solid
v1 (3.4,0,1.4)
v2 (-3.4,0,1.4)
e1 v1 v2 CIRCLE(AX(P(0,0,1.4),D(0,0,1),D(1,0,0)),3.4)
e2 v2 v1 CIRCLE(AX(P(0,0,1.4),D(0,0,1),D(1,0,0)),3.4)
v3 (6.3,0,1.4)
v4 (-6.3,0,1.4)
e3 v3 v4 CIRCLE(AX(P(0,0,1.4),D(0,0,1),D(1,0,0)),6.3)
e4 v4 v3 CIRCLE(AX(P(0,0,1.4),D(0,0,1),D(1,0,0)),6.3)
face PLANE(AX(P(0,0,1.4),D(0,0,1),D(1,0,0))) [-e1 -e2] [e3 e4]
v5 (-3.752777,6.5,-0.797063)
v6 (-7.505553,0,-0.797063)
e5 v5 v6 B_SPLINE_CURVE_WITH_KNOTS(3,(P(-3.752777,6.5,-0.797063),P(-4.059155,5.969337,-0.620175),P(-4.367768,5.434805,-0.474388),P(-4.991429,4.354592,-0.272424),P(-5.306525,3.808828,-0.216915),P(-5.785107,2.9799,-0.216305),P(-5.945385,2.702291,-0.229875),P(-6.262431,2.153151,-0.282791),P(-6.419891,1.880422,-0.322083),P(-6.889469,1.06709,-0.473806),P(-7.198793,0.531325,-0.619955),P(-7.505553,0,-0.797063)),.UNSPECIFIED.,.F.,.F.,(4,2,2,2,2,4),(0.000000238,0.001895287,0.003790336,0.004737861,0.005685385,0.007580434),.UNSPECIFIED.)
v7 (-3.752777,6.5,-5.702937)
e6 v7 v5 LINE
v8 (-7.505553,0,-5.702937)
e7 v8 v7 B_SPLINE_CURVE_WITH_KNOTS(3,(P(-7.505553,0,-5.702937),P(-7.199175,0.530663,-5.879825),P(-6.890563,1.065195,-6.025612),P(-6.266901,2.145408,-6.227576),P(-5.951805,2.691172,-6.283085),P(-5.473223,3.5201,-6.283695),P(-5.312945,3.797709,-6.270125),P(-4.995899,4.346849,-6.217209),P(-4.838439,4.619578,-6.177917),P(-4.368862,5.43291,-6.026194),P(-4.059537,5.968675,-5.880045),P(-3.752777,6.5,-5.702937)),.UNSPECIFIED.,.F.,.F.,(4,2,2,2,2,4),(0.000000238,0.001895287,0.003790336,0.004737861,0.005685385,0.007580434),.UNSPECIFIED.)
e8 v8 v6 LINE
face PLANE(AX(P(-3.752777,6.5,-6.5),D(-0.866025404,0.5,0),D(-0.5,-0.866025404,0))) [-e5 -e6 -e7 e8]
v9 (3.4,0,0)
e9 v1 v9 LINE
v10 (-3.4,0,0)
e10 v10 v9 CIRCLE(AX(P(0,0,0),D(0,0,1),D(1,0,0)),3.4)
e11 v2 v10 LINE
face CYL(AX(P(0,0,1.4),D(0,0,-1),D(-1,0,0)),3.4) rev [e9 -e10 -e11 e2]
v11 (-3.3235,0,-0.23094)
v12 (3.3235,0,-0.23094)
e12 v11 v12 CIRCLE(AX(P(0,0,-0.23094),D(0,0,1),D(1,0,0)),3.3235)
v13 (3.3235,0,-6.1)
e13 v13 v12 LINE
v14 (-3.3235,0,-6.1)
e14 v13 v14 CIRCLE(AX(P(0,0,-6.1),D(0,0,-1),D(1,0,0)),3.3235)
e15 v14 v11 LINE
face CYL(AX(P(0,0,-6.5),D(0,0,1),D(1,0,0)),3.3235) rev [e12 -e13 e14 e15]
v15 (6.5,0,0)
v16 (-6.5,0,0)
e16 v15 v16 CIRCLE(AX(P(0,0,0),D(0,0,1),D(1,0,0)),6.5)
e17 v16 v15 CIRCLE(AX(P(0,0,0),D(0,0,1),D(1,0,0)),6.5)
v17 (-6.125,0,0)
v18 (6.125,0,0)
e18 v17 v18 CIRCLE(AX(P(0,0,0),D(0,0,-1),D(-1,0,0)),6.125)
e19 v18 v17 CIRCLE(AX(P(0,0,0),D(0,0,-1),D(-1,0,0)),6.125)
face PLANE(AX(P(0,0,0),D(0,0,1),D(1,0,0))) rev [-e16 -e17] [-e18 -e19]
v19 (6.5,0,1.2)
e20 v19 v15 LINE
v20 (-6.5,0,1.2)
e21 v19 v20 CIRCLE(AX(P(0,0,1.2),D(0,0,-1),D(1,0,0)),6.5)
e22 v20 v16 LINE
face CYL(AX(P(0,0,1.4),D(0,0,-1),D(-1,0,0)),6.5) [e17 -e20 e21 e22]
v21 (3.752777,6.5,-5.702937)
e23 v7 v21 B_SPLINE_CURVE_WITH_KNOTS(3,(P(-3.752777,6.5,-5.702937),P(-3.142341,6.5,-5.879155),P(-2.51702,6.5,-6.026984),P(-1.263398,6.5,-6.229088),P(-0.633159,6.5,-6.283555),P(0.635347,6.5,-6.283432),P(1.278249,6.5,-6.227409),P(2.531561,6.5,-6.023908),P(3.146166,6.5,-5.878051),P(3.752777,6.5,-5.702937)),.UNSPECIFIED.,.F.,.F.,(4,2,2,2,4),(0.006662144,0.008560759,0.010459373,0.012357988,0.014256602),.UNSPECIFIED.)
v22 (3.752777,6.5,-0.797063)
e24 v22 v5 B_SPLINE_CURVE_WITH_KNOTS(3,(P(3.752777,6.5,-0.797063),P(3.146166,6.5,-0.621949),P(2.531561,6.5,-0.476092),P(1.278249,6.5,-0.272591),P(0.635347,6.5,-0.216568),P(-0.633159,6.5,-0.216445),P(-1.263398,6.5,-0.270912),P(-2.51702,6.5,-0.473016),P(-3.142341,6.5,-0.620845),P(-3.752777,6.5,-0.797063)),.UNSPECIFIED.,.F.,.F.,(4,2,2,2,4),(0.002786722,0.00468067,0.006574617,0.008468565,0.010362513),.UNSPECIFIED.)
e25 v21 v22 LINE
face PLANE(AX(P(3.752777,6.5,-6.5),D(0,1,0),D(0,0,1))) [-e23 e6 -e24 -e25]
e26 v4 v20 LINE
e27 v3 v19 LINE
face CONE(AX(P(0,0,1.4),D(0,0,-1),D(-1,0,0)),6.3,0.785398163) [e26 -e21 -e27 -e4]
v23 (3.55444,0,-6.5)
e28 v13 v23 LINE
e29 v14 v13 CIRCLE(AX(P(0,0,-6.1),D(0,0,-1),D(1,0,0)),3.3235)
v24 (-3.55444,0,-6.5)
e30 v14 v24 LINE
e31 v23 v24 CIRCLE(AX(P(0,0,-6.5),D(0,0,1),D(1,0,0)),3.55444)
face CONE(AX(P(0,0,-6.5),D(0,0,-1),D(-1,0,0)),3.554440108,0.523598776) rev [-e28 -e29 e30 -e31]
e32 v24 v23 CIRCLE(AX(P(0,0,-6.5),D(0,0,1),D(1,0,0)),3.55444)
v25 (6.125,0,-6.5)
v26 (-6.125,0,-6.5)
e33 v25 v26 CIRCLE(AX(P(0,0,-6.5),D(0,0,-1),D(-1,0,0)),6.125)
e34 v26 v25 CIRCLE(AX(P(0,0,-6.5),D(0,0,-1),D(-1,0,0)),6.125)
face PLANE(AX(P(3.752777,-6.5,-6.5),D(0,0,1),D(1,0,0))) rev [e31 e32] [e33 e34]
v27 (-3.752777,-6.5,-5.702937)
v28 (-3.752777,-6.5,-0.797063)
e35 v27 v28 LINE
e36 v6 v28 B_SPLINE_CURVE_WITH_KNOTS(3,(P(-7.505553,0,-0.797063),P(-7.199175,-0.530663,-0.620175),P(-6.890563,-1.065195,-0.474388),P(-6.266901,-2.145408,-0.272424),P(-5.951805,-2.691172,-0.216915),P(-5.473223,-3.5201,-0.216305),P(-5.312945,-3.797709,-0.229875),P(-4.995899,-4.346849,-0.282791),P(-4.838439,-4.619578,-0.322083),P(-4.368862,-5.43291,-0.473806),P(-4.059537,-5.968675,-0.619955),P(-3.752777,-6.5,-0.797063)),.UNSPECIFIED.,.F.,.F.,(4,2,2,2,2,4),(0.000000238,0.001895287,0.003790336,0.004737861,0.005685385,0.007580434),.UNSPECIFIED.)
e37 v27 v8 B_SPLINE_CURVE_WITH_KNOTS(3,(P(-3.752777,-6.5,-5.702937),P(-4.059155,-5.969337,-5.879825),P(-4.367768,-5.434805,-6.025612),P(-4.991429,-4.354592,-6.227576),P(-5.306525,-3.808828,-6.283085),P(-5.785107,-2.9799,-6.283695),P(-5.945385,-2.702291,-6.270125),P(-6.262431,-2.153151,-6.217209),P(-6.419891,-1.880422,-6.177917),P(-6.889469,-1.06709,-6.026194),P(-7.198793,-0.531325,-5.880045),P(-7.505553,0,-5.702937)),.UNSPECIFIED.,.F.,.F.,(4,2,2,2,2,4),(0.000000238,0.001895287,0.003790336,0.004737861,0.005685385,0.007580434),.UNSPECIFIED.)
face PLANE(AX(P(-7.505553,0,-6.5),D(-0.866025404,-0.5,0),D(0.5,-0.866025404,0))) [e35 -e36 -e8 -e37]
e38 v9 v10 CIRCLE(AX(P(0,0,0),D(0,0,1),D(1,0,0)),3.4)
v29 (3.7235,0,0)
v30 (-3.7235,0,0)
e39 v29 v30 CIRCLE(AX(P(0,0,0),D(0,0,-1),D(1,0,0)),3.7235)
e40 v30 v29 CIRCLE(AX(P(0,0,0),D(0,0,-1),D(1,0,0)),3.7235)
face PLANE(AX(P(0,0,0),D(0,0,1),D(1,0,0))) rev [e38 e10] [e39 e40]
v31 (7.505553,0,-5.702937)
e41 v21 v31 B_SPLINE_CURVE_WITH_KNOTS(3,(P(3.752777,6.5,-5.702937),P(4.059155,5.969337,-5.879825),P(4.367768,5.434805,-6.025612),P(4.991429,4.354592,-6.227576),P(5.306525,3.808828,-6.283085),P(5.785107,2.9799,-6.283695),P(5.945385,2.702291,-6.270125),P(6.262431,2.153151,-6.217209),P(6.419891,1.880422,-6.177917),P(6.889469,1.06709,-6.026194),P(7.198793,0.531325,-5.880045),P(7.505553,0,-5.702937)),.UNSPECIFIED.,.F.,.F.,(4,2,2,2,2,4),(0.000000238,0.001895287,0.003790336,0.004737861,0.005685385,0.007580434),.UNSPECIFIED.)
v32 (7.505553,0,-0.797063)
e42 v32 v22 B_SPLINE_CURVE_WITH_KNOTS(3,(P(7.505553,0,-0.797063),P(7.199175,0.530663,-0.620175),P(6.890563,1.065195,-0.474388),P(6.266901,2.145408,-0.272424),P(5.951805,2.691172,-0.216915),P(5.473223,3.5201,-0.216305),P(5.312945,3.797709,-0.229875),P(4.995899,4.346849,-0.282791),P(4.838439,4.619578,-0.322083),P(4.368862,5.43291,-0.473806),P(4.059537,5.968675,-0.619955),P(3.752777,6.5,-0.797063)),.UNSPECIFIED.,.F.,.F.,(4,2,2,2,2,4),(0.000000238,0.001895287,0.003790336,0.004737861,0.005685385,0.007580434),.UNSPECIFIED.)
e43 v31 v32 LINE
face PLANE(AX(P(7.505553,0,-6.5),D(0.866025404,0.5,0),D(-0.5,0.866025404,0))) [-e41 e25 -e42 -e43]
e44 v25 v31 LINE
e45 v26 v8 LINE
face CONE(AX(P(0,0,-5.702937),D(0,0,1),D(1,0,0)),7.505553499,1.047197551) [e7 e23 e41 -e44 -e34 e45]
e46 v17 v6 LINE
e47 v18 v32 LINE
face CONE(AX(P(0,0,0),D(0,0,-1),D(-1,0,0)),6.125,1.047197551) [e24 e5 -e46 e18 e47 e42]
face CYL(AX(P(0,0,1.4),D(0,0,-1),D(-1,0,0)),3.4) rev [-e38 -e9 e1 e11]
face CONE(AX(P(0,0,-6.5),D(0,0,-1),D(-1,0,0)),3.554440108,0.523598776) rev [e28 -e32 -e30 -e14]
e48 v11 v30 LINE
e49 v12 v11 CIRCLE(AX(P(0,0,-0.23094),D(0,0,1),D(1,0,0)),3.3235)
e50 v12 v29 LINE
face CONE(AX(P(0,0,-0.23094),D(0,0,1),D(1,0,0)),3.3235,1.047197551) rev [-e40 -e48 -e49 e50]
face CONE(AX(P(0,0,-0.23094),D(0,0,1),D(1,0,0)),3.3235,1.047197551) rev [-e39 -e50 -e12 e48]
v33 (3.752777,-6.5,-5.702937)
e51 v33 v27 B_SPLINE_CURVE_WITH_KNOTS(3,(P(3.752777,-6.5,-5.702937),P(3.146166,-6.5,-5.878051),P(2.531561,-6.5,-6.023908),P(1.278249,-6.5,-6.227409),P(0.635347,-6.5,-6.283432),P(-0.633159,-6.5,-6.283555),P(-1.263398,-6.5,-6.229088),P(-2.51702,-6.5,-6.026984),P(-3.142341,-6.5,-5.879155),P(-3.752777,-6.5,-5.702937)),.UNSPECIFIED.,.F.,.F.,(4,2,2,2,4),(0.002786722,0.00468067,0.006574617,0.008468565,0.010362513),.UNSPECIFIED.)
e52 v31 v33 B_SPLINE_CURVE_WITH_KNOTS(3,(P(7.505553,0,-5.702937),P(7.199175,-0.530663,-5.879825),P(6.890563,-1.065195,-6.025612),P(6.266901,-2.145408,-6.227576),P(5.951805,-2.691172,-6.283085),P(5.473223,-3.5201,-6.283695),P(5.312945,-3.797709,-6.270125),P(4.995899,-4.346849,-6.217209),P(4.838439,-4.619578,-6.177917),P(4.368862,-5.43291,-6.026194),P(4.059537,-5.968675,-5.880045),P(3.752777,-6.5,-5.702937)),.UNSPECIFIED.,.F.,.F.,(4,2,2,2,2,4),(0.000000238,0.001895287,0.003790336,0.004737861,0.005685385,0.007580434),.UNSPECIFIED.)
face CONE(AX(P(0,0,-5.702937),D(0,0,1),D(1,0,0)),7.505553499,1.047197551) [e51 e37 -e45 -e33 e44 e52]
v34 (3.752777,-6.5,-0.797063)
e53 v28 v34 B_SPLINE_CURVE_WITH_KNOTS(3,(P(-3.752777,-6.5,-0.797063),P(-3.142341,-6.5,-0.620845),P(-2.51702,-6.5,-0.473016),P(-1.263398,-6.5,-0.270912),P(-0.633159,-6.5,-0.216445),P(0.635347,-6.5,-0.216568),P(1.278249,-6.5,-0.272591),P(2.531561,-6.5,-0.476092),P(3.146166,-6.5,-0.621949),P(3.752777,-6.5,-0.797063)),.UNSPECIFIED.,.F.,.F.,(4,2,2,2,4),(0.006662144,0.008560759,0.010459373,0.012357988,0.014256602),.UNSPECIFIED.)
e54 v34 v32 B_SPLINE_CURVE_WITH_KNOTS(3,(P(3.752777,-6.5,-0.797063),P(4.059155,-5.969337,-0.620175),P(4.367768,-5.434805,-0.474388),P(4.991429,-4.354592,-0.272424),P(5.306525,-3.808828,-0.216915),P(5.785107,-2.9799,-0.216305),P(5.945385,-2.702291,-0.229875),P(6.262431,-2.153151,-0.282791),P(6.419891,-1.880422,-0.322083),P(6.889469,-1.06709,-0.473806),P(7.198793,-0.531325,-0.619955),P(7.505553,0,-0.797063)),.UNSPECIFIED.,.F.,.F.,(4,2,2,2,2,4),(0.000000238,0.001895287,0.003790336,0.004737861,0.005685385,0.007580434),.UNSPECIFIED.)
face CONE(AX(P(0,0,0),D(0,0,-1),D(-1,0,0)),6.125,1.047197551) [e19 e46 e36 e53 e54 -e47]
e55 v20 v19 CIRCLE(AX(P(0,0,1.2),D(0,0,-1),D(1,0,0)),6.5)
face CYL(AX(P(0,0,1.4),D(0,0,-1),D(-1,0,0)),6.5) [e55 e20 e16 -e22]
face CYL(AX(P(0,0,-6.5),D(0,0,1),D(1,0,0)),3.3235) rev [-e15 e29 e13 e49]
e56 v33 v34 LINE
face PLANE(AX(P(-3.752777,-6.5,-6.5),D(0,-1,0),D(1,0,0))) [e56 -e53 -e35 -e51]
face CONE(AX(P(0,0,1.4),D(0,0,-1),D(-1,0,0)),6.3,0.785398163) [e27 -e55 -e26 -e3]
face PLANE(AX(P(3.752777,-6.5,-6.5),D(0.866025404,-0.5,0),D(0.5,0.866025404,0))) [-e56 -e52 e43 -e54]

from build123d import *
from OCP.BRepFilletAPI import BRepFilletAPI_MakeChamfer

# Parameters (mm, degrees)
SKETCH1_R        = 3.3235
BASENUT_DEPTH    = 6.5
ENDCHAMFER_SIZE  = 0.4
ENDCHAMFER_SIZE2 = 0.230940108
SKETCH_1_R       = 6.5
SKETCH_1_R_2     = 3.4
EXTRUDE_1_DEPTH  = 1.4
CHAMFER_1_SIZE   = 0.2


with BuildPart() as part:
    # Sketch1 → BaseNut (new body)
    with BuildSketch(Plane.XY):
        Polygon((3.75277675, -6.5), (7.505553499, 0), (3.75277675, 6.5), (-3.75277675, 6.5), (-7.505553499, 0), (-3.75277675, -6.5), align=None)
        Circle(SKETCH1_R, mode=Mode.SUBTRACT)
    extrude(amount=-BASENUT_DEPTH)

    # Sketch2 → Double-Chamfer (revolve, cut)
    with BuildSketch(Plane(origin=(0, 0, 0), x_dir=(1, 0, 0), z_dir=(0, 1, 0))):
        Polygon((-7.505553499, 6.5), (-6.125, 6.5), (-7.505553499, 5.702937065), align=None)
        Polygon((-7.505553499, 0.797062935), (-7.505553499, 0), (-6.125, 0), align=None)
    revolve(axis=Axis((0, 0, -3.375940562), (0, 0, 1)), mode=Mode.SUBTRACT)

    # EndChamfer: one chamfer whose edges measure the first distance from different faces: ONE call of the kernel's chamfer builder (chamfer() names one face for all edges)
    endchamfer_edges_1 = [part.edges().sort_by_distance(p)[0] for p in [
        (-3.3235, 0, -6.5),
    ]]
    endchamfer_side_1 = [part.faces().sort_by_distance(p)[0] for p in [
        (-3.3235, 0, -3.25),
    ]]
    endchamfer_edges_2 = [part.edges().sort_by_distance(p)[0] for p in [
        (-3.3235, 0, 0),
    ]]
    endchamfer_side_2 = [part.faces().sort_by_distance(p)[0] for p in [
        (5.951758839, 0, 0),
    ]]
    endchamfer = BRepFilletAPI_MakeChamfer(part.part.solid().wrapped)
    for e in endchamfer_edges_1:
        endchamfer.Add(ENDCHAMFER_SIZE, ENDCHAMFER_SIZE2, e.wrapped, endchamfer_side_1[0].wrapped)  # the first distance lies on this face
    for e in endchamfer_edges_2:
        endchamfer.Add(ENDCHAMFER_SIZE, ENDCHAMFER_SIZE2, e.wrapped, endchamfer_side_2[0].wrapped)  # the first distance lies on this face
    add(Compound.cast(endchamfer.Shape()), mode=Mode.REPLACE)

    # 草图1 → 凸台-拉伸1 (add)
    with BuildSketch(Plane.XY):
        Circle(SKETCH_1_R)
        Circle(SKETCH_1_R_2, mode=Mode.SUBTRACT)
    extrude(amount=EXTRUDE_1_DEPTH)

    # 倒角1
    chamfer_1_edges = [part.edges().sort_by_distance(p)[0] for p in [
        (-6.5, 0, 1.4),
    ]]
    chamfer(chamfer_1_edges, length=CHAMFER_1_SIZE)


solid = part.part
